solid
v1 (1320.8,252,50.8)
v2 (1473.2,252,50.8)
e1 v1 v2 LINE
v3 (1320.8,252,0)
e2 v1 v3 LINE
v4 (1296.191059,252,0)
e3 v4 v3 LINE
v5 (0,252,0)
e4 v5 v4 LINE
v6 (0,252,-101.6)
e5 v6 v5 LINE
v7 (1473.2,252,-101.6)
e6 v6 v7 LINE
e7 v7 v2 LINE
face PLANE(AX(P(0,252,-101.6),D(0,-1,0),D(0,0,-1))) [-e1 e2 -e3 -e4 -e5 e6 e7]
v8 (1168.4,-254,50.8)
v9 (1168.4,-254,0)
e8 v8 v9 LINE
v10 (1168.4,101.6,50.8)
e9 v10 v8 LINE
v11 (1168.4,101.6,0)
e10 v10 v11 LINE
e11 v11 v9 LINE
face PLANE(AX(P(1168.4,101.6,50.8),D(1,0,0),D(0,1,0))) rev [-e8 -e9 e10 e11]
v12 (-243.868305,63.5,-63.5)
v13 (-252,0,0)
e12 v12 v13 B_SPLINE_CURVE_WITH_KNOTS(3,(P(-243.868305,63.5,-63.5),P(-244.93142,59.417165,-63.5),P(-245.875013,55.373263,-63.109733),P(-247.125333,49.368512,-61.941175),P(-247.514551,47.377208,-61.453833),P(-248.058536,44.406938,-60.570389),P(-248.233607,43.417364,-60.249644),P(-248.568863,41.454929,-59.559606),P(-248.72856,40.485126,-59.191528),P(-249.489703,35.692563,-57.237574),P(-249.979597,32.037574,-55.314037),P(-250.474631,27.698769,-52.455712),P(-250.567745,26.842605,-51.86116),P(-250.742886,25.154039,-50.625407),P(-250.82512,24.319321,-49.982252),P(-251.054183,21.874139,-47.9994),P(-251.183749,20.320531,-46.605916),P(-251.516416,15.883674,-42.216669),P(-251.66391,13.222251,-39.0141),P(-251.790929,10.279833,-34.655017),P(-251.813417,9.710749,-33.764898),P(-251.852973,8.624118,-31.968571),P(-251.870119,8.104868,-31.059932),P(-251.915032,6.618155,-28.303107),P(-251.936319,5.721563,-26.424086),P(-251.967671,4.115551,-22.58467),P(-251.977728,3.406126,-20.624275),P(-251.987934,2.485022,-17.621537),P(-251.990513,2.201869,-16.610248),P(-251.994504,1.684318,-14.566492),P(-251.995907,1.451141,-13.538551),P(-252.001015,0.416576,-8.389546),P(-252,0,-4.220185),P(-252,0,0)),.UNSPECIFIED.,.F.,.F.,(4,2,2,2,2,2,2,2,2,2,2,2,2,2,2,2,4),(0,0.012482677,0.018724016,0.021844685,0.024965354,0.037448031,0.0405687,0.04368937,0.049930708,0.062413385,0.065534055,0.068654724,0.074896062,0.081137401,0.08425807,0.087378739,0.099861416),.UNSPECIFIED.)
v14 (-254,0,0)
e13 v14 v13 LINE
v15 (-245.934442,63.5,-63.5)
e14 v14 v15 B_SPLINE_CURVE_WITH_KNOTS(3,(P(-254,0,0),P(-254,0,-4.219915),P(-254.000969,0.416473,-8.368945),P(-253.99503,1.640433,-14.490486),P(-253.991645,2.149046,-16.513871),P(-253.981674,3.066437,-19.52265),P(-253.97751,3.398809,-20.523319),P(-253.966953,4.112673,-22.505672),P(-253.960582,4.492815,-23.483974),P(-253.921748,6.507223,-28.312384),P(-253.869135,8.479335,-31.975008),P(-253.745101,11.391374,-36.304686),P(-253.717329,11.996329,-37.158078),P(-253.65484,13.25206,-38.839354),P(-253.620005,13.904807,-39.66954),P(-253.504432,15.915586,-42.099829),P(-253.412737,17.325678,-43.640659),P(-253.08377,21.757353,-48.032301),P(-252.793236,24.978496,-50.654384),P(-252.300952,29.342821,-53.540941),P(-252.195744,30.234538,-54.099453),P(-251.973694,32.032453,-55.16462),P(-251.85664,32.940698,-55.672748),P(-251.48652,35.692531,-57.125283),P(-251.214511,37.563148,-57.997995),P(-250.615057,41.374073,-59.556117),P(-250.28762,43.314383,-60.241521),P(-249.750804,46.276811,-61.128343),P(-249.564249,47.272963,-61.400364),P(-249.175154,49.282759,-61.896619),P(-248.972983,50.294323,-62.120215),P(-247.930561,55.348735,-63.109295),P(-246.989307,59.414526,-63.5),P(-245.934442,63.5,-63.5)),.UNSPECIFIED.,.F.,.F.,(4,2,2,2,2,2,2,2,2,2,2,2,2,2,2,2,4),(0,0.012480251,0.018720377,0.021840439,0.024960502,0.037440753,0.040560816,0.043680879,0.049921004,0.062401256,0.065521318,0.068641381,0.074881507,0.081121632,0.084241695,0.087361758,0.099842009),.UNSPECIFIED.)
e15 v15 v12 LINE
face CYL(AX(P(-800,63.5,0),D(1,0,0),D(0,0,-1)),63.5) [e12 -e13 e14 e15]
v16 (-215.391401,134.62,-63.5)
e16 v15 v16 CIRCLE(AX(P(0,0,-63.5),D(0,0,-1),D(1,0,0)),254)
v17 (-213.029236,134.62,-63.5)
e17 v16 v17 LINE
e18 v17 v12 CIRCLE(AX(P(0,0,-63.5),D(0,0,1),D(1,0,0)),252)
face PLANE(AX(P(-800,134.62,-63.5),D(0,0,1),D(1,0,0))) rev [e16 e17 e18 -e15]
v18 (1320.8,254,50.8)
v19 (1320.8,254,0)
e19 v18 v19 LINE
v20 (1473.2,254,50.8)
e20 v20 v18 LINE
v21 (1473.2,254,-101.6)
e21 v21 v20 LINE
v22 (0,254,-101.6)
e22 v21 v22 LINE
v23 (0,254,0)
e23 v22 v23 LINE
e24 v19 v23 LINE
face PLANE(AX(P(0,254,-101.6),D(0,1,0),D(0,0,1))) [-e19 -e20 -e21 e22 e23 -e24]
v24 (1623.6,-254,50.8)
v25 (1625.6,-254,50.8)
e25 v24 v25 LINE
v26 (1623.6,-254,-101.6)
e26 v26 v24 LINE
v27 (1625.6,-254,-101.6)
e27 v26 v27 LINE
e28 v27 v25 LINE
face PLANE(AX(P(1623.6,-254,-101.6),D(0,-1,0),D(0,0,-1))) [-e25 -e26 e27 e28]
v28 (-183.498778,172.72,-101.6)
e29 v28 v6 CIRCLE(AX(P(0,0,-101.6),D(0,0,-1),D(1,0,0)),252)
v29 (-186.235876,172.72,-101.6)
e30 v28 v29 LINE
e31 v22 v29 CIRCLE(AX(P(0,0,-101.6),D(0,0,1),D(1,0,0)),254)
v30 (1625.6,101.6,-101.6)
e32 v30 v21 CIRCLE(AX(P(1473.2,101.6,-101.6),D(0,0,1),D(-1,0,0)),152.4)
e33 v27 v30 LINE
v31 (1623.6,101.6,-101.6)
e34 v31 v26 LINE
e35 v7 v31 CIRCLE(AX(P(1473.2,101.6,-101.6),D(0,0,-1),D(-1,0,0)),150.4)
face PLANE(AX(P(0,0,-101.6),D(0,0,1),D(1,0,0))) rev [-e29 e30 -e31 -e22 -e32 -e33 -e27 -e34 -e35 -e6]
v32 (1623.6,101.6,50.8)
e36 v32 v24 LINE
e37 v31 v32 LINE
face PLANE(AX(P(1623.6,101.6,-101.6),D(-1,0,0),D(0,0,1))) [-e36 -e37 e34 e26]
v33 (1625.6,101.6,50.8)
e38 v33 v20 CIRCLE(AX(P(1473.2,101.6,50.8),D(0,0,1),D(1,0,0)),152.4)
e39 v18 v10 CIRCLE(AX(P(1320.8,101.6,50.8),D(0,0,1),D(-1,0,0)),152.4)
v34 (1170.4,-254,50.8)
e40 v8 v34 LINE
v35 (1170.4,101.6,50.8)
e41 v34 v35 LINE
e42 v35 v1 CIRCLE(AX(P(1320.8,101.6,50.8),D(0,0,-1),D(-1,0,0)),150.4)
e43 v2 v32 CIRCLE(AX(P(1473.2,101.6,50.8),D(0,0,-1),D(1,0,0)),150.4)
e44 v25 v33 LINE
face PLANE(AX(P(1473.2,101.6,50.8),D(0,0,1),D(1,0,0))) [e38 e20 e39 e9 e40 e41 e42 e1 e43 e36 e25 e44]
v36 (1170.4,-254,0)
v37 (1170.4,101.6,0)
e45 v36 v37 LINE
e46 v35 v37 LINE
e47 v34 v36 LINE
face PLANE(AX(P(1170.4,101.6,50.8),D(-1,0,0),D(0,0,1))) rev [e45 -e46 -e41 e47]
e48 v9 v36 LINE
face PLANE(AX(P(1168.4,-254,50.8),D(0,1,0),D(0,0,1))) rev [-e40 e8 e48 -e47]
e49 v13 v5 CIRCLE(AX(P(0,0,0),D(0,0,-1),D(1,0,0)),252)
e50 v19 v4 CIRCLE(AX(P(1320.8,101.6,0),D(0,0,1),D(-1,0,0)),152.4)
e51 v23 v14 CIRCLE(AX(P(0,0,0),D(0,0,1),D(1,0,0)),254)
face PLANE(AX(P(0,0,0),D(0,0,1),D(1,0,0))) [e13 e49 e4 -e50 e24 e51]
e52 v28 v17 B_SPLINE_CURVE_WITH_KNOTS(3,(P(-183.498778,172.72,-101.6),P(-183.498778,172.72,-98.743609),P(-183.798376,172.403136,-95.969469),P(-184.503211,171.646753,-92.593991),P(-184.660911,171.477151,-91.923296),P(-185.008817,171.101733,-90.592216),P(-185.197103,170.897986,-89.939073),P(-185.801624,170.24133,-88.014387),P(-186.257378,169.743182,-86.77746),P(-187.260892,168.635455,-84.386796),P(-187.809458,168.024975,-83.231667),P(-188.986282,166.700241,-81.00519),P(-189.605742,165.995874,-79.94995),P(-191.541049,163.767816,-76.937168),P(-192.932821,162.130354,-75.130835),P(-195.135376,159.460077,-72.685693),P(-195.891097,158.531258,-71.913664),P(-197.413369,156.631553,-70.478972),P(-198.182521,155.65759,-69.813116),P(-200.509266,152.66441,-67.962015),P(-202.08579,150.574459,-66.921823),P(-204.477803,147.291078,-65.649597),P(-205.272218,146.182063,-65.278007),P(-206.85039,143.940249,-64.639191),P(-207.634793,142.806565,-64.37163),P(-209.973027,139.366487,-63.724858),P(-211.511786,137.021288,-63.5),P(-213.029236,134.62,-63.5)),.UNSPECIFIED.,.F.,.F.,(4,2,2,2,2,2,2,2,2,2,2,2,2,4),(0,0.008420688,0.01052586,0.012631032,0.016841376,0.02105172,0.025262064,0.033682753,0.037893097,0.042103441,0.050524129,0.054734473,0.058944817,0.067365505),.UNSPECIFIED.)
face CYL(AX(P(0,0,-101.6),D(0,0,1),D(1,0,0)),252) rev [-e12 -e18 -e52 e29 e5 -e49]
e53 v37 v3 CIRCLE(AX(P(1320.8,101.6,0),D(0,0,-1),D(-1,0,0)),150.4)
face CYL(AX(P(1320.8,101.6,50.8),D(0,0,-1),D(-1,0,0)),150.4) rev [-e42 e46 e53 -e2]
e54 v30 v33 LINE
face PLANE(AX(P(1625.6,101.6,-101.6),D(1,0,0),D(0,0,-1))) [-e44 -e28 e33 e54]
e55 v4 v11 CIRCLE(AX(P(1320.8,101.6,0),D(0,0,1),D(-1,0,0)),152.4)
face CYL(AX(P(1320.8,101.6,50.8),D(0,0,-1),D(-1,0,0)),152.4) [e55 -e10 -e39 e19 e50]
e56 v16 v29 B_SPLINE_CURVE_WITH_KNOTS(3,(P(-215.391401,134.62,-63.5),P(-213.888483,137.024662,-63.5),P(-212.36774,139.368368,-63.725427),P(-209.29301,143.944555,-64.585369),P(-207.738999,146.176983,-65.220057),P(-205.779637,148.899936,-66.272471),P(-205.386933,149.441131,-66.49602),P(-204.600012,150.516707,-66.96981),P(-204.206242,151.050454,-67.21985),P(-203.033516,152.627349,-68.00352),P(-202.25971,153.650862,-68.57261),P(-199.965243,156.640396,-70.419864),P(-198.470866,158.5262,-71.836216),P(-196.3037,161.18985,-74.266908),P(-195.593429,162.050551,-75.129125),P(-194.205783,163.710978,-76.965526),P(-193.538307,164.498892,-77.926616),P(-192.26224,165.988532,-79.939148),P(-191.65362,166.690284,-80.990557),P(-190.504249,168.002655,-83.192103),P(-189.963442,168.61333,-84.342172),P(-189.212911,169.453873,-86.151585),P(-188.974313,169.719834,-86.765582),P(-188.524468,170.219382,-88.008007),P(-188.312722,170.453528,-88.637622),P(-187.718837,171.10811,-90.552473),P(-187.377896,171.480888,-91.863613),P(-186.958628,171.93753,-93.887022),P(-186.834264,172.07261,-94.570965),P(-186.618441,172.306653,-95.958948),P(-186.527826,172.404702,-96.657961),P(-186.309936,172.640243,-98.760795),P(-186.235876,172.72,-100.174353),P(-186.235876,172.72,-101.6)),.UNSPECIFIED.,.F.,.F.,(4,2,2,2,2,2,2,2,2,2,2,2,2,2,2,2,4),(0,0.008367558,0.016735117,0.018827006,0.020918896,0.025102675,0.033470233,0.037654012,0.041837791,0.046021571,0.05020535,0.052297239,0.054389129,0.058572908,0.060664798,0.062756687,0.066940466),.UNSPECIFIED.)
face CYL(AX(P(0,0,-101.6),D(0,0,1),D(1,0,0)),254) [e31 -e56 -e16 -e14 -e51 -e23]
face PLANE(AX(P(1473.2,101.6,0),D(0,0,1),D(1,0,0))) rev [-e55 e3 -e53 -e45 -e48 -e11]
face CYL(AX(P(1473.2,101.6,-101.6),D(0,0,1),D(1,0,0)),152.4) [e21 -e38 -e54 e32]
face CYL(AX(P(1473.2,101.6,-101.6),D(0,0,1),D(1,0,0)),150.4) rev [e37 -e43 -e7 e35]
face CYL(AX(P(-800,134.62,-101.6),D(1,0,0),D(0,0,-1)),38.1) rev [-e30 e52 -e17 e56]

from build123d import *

# Parameters (mm, degrees)
BOSS_EXTRUDE1_DEPTH = 101.6
BOSS_EXTRUDE2_START = 50.8
BOSS_EXTRUDE2_DEPTH = 50.8
CUT_EXTRUDE1_DEPTH  = 800


with BuildPart() as part:
    # Sketch1 → Boss-Extrude1 (new body)
    with BuildSketch(Plane.XY):
        with BuildLine():
            Line((0, 254), (1473.2, 254))
            ThreePointArc((1473.2, 254), (1580.963073453, 209.363073453), (1625.6, 101.6))
            Line((1625.6, 101.6), (1625.6, -254))
            Line((1625.6, -254), (1623.6, -254))
            Line((1623.6, -254), (1623.6, 101.6))
            ThreePointArc((1623.6, 101.6), (1579.54885989, 207.94885989), (1473.2, 252))
            Line((1473.2, 252), (0, 252))
            ThreePointArc((0, 252), (-178.190908859, 178.190908859), (-252, 0))
            Line((-252, 0), (-254, 0))
            ThreePointArc((-254, 0), (-179.605122421, 179.605122421), (0, 254))
        make_face()
    extrude(amount=-BOSS_EXTRUDE1_DEPTH)

    # Sketch2 → Boss-Extrude2 (add)
    with BuildSketch(Plane.XY.offset(BOSS_EXTRUDE2_START)):
        with BuildLine():
            Line((1625.6, -254), (1625.6, 101.6))
            ThreePointArc((1625.6, 101.6), (1580.963073453, 209.363073453), (1473.2, 254))
            Line((1473.2, 254), (1320.8, 254))
            ThreePointArc((1320.8, 254), (1213.036926547, 209.363073453), (1168.4, 101.6))
            Line((1168.4, 101.6), (1168.4, -254))
            Line((1168.4, -254), (1170.4, -254))
            Line((1170.4, -254), (1170.4, 101.6))
            ThreePointArc((1170.4, 101.6), (1214.45114011, 207.94885989), (1320.8, 252))
            Line((1320.8, 252), (1473.2, 252))
            ThreePointArc((1473.2, 252), (1579.54885989, 207.94885989), (1623.6, 101.6))
            Line((1623.6, 101.6), (1623.6, -254))
            Line((1623.6, -254), (1625.6, -254))
        make_face()
    extrude(amount=-BOSS_EXTRUDE2_DEPTH)

    # Sketch3 → Cut-Extrude1 (cut)
    with BuildSketch(Plane(origin=(0, 0, 0), x_dir=(0, 0, -1), z_dir=(1, 0, 0))):
        with BuildLine():
            Line((101.6, 172.72), (101.6, 0))
            Line((101.6, 0), (0, 0))
            ThreePointArc((0, 0), (44.901280605, 18.598719395), (63.5, 63.5))
            Line((63.5, 63.5), (63.5, 134.62))
            ThreePointArc((63.5, 134.62), (74.659231637, 161.560768363), (101.6, 172.72))
        make_face()
    extrude(amount=-CUT_EXTRUDE1_DEPTH, mode=Mode.SUBTRACT)


solid = part.part
